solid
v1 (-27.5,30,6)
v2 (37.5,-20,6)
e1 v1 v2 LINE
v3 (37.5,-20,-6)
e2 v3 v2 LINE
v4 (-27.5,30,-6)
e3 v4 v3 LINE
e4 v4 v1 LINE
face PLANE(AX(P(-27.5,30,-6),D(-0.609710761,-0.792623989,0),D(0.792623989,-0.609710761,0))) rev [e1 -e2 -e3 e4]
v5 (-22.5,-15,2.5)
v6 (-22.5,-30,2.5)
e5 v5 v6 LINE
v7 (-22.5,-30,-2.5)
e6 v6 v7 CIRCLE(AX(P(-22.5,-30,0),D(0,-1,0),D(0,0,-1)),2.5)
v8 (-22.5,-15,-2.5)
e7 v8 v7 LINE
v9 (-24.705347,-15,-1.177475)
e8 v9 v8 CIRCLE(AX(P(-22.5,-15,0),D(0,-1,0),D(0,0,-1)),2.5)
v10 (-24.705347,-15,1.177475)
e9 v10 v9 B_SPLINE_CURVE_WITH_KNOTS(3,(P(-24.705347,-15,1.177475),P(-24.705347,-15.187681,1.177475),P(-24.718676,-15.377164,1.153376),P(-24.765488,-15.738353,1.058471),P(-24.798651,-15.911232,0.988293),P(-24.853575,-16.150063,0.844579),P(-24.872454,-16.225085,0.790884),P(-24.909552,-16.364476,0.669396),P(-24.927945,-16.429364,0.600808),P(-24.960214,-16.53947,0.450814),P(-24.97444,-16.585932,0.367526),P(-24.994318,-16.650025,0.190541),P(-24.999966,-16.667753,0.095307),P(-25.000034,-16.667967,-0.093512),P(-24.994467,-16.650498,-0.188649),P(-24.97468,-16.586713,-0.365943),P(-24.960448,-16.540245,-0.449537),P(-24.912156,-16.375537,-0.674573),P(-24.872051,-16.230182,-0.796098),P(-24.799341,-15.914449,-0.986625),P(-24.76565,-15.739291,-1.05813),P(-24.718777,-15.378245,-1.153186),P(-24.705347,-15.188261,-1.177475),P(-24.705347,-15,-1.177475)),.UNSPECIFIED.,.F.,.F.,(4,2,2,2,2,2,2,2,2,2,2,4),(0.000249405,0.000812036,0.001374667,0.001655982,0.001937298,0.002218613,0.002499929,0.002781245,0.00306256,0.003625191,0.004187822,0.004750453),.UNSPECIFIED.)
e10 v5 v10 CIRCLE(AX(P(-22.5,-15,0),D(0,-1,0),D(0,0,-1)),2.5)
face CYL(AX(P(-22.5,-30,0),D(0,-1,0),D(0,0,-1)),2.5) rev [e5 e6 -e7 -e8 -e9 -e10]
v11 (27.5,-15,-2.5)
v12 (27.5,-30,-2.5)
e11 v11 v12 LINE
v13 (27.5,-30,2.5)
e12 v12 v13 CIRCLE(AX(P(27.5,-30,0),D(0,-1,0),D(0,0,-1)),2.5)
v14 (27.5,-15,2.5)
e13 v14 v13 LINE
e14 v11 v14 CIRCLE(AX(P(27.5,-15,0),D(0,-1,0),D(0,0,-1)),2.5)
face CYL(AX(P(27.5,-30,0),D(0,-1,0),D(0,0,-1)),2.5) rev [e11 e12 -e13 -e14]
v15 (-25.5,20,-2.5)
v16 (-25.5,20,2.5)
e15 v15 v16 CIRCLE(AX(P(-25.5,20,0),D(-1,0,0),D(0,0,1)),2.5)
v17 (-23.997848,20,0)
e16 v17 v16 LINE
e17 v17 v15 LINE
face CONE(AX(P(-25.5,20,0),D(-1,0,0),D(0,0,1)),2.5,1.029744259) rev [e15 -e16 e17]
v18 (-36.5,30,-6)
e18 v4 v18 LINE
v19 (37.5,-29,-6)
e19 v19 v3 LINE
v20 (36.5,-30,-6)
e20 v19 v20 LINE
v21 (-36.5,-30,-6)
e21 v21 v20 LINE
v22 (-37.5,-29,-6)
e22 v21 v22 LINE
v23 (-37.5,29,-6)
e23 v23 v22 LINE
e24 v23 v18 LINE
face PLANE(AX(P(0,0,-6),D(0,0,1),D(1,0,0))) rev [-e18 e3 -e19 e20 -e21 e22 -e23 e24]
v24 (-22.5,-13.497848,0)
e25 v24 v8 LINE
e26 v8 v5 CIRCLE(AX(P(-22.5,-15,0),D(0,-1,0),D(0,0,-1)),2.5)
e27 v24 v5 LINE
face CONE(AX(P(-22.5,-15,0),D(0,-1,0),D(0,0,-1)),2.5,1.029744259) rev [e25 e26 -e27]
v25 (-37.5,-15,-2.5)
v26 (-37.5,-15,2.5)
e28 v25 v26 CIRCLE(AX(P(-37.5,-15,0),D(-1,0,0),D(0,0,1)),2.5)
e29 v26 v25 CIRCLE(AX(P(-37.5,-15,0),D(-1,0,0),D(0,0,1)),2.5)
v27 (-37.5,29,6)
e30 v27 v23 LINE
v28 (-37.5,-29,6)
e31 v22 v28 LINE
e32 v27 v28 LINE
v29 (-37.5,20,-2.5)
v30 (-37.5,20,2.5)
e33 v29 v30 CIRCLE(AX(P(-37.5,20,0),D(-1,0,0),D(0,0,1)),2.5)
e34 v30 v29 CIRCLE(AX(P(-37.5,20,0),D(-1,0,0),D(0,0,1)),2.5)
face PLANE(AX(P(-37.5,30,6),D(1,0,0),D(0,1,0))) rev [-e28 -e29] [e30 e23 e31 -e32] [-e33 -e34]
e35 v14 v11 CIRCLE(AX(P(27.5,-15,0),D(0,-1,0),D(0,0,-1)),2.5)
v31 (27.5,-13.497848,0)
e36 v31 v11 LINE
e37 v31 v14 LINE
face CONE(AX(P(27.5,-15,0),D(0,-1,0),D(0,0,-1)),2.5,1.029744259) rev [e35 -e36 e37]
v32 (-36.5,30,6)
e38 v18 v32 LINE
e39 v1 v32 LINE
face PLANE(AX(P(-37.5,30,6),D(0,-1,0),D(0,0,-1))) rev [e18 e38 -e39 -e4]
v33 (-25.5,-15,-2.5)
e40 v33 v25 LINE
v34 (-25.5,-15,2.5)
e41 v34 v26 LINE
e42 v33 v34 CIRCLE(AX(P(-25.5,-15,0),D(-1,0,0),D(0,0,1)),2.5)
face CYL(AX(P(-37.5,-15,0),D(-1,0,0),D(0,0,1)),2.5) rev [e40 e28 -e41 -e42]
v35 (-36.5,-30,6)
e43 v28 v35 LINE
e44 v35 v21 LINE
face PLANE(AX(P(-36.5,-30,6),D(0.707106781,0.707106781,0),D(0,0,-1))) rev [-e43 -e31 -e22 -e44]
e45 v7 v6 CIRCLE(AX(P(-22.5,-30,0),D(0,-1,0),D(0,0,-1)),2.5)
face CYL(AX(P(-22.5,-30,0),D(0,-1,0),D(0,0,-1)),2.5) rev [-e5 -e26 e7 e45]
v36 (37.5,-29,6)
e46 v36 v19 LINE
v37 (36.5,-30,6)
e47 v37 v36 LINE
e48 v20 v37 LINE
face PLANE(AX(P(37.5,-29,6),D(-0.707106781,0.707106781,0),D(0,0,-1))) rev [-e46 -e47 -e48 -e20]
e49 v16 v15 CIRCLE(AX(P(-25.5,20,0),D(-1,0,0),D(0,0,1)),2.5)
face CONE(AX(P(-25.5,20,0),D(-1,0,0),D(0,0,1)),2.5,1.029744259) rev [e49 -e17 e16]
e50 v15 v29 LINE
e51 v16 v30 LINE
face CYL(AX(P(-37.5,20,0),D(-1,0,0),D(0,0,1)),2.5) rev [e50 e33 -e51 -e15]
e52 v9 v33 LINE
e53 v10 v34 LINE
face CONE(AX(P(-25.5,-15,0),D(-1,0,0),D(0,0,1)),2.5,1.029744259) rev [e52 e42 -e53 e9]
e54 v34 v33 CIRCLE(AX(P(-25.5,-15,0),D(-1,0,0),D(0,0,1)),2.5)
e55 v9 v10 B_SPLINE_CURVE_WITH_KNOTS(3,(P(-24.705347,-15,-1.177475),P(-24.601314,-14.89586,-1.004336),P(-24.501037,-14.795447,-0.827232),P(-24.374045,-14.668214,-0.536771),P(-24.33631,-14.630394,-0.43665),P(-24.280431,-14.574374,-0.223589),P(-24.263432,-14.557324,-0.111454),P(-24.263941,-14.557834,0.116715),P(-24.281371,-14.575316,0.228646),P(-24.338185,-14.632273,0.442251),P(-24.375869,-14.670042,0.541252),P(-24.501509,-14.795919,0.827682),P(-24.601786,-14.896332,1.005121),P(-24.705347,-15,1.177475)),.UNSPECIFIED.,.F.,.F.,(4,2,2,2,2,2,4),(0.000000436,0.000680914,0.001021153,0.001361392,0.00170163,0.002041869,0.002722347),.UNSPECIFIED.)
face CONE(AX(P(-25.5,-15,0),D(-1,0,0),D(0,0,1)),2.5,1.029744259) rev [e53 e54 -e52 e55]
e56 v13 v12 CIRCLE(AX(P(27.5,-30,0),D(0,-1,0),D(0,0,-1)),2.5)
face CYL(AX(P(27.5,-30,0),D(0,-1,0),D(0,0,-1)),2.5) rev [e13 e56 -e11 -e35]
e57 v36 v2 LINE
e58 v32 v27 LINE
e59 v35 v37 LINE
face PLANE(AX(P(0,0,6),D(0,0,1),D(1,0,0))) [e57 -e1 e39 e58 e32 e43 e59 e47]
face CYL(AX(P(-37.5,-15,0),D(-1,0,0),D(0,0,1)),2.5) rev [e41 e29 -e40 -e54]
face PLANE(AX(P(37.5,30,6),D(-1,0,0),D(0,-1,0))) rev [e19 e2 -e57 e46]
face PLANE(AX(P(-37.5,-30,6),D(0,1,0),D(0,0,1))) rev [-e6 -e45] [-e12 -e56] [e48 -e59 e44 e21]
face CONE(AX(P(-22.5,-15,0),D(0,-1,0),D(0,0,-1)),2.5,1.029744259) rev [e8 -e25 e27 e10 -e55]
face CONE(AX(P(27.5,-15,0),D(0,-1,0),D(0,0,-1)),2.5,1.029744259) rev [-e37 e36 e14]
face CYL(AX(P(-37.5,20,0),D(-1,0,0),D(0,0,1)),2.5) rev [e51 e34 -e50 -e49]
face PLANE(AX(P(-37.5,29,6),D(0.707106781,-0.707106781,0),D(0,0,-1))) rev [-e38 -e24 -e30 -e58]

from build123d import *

# Parameters (mm, degrees)
SKETCH1_W             = 75
SKETCH1_H             = 60
BOSS_EXTRUDE1_DEPTH   = 6
CUT_EXTRUDE1_DEPTH    = 50.5
M6_TAPPED_HOLE1_D     = 5
M6_TAPPED_HOLE1_DEPTH = 12
M6_TAPPED_HOLE1_TIP   = 1.502151548
M6_TAPPED_HOLE2_D     = 5
M6_TAPPED_HOLE2_DEPTH = 15
M6_TAPPED_HOLE2_TIP   = 1.502151548
CHAMFER1_SIZE         = 1


with BuildPart() as part:
    # Sketch1 → Boss-Extrude1 (new, symmetric)
    with BuildSketch(Plane.XY):
        Rectangle(SKETCH1_W, SKETCH1_H)
    extrude(amount=BOSS_EXTRUDE1_DEPTH, both=True)

    # Sketch2 → Cut-Extrude1 (cut, through all)
    with BuildSketch(Plane.XY.offset(6)):
        Polygon((-27.5, 30), (37.5, -20), (37.5, 30), align=None)
    extrude(amount=-CUT_EXTRUDE1_DEPTH, mode=Mode.SUBTRACT)

    # M6 Tapped Hole1
    with Locations(Plane.ZY.offset(37.5)):
        with Locations((0, 20), (0, -15)):
            Hole(M6_TAPPED_HOLE1_D / 2, depth=M6_TAPPED_HOLE1_DEPTH)
            with Locations((0, 0, -(M6_TAPPED_HOLE1_DEPTH + M6_TAPPED_HOLE1_TIP / 2))):  # 118° drill point
                Cone(0, M6_TAPPED_HOLE1_D / 2, M6_TAPPED_HOLE1_TIP, mode=Mode.SUBTRACT)

    # M6 Tapped Hole2
    with Locations(Plane(origin=(0, -30, 0), x_dir=(-1, 0, 0), z_dir=(0, -1, 0))):
        with Locations((22.5, 0), (-27.5, 0)):
            Hole(M6_TAPPED_HOLE2_D / 2, depth=M6_TAPPED_HOLE2_DEPTH)
            with Locations((0, 0, -(M6_TAPPED_HOLE2_DEPTH + M6_TAPPED_HOLE2_TIP / 2))):  # 118° drill point
                Cone(0, M6_TAPPED_HOLE2_D / 2, M6_TAPPED_HOLE2_TIP, mode=Mode.SUBTRACT)

    # Chamfer1
    chamfer1_edges = [part.edges().sort_by_distance(p)[0] for p in [
        (37.5, -30, 0),
        (-37.5, -30, 0),
        (-37.5, 30, 0),
    ]]
    chamfer(chamfer1_edges, length=CHAMFER1_SIZE)


solid = part.part
